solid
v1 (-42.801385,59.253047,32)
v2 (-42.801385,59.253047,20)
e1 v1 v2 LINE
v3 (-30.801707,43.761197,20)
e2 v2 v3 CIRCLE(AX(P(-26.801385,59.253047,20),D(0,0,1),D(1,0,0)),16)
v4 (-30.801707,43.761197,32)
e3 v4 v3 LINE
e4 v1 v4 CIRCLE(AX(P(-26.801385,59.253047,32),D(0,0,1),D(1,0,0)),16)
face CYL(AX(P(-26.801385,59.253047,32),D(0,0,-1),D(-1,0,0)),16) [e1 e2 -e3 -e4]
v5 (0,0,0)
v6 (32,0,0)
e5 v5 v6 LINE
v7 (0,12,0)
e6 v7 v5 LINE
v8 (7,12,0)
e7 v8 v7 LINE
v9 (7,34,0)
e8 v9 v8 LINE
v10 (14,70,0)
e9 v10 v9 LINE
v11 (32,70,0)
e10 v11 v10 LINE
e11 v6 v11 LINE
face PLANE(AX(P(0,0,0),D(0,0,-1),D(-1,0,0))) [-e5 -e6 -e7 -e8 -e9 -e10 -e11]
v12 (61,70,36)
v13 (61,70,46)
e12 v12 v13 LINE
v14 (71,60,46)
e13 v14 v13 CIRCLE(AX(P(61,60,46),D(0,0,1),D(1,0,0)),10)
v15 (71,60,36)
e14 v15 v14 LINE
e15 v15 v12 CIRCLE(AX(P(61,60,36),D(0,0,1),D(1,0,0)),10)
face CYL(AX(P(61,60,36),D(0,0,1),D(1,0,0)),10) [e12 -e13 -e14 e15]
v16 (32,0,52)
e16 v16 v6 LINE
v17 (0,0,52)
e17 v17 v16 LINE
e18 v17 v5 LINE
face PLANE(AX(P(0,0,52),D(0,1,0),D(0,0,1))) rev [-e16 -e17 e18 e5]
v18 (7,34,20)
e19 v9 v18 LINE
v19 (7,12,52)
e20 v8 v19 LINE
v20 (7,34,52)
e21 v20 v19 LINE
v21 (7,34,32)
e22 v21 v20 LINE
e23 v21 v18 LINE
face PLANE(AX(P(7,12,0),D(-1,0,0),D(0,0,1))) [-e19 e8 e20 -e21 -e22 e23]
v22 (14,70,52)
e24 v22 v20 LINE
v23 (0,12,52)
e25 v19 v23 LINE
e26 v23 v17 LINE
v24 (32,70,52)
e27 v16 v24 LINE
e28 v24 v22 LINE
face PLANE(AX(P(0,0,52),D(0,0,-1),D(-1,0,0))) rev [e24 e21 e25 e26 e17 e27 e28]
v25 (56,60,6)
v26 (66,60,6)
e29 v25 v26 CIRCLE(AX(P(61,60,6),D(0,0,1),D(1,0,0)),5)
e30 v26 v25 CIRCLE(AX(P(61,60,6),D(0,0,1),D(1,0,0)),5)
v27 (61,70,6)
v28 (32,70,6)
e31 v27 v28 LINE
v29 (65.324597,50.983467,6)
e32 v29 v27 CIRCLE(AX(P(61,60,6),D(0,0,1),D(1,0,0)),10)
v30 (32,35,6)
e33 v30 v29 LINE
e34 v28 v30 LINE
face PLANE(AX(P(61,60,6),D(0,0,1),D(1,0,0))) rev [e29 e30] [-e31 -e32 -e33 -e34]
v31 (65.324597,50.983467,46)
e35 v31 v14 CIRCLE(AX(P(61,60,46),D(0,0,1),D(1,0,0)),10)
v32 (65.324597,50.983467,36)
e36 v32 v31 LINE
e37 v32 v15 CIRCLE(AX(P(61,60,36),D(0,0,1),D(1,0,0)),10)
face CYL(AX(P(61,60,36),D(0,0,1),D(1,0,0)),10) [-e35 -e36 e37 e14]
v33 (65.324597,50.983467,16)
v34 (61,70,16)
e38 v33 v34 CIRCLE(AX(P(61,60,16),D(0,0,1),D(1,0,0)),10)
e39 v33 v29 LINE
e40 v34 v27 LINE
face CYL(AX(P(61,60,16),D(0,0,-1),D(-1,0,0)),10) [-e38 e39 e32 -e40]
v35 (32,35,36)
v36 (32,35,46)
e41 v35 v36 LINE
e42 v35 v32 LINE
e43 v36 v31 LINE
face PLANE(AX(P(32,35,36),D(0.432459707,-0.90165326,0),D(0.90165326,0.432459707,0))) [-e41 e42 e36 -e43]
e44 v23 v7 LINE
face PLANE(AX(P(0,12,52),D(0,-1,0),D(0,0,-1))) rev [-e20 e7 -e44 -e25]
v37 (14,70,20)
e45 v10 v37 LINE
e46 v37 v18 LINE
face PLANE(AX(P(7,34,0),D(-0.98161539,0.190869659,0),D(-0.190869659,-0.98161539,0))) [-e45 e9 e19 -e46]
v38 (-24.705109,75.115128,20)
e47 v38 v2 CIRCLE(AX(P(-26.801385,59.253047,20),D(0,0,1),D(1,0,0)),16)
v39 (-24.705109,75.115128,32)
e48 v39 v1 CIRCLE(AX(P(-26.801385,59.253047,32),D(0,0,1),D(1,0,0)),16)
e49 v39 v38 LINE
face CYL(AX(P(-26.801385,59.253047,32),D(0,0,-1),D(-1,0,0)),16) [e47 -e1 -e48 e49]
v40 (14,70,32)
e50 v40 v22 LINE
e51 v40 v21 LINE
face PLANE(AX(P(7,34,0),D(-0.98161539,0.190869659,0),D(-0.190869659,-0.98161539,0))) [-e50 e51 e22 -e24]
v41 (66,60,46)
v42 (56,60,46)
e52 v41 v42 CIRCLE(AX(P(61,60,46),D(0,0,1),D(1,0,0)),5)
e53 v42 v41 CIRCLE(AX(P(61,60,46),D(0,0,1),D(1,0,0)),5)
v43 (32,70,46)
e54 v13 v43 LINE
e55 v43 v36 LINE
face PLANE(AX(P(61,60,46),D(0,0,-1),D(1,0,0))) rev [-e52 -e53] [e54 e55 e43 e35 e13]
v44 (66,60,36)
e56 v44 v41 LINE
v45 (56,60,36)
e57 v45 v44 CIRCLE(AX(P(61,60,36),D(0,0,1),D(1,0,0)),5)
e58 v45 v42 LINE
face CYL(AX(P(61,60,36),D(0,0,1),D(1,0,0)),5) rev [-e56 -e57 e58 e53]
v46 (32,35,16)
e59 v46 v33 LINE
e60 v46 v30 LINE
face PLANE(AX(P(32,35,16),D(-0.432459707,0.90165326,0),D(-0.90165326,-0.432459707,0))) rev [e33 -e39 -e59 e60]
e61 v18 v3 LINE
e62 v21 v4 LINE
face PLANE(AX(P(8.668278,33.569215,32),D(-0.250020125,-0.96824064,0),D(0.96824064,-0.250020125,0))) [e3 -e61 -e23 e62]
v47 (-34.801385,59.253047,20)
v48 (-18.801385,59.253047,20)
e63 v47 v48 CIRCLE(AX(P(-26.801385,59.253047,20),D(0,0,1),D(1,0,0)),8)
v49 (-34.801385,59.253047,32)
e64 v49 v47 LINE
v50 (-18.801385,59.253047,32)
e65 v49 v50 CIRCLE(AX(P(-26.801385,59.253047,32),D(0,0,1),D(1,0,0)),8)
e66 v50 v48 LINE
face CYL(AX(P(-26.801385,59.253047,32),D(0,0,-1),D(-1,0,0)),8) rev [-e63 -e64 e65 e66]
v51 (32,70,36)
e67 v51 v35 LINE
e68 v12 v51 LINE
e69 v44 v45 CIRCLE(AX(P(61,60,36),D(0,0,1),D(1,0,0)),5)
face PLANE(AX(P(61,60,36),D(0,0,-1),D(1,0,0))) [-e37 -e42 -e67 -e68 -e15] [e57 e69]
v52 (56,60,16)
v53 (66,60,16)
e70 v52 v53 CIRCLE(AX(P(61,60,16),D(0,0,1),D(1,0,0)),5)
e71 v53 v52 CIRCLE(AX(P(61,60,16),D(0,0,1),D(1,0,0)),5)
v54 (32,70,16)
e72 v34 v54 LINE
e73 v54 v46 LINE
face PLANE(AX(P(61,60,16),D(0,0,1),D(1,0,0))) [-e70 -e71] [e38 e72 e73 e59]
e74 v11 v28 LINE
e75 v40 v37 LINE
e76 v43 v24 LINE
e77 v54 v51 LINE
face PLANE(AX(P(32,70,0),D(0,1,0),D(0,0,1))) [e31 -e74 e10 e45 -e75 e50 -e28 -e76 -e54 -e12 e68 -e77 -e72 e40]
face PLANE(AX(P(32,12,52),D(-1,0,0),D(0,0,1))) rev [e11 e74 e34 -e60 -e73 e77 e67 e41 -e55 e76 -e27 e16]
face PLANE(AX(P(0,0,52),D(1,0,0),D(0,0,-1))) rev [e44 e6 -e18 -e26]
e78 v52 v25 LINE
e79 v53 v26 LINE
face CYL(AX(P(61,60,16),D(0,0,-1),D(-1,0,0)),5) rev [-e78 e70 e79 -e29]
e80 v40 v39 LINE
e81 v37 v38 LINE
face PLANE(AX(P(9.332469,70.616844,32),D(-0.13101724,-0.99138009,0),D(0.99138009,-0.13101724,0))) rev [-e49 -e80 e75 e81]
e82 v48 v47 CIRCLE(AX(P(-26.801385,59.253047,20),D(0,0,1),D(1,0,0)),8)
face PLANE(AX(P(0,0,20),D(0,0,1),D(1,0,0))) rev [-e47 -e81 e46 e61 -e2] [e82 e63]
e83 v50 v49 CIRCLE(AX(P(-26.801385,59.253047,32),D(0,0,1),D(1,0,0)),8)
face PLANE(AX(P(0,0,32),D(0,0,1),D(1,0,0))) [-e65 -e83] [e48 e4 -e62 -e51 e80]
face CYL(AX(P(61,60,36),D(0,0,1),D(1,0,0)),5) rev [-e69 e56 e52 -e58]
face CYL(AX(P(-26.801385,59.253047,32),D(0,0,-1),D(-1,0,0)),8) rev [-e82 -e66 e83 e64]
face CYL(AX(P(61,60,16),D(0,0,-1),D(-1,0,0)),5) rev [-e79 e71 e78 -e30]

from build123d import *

# Parameters (mm, degrees)
BASE_BLOCK_SKETCH_W = 32
BASE_BLOCK_SKETCH_H = 12
BASE_BLOCK_DEPTH    = 52
UPRIGHT_BODY_DEPTH  = 52
CLEVIS_LUG_SKETCH_R = 5
CLEVIS_LUG_DEPTH    = 10
PIVOT_ARM_SKETCH_R  = 8
PIVOT_ARM_DEPTH     = 6


with BuildPart() as part:
    # Base Block Sketch → Base Block (new body)
    with BuildSketch(Plane.XY):
        with Locations((16, 6)):
            Rectangle(BASE_BLOCK_SKETCH_W, BASE_BLOCK_SKETCH_H)
    extrude(amount=BASE_BLOCK_DEPTH)

    # Upright Profile Sketch → Upright Body (add)
    with BuildSketch(Plane.XY.offset(52)):
        Polygon((32, 12), (32, 70), (14, 70), (7, 34), (7, 12), align=None)
    extrude(amount=-UPRIGHT_BODY_DEPTH)

    # Clevis Lug Sketch → Clevis Lug (add)
    with BuildSketch(Plane.XY.offset(6)):
        with BuildLine():
            Line((32, 70), (61, 70))
            ThreePointArc((61, 70), (70.751033946, 62.217506931), (65.324597071, 50.983467397))
            Line((65.324597071, 50.983467397), (32, 35))
            Line((32, 35), (32, 70))
        make_face()
        with Locations((61, 60)):
            Circle(CLEVIS_LUG_SKETCH_R, mode=Mode.SUBTRACT)
    clevis_lug = extrude(amount=CLEVIS_LUG_DEPTH)

    # Clevis Lug Mirror: Clevis Lug across plane
    add(clevis_lug.mirror(Plane.XY.offset(26)))

    # Pivot Arm Sketch → Pivot Arm (add, symmetric)
    with BuildSketch(Plane.XY.offset(26)):
        with BuildLine():
            Line((14, 70), (-24.705108972, 75.115128486))
            ThreePointArc((-24.705108972, 75.115128486), (-42.507231042, 62.306961592), (-30.8017068, 43.761196803))
            Line((-30.8017068, 43.761196803), (7, 34))
            Line((7, 34), (14, 70))
        make_face()
        with Locations((-26.801384807, 59.253047046)):
            Circle(PIVOT_ARM_SKETCH_R, mode=Mode.SUBTRACT)
    extrude(amount=PIVOT_ARM_DEPTH, both=True)


solid = part.part
